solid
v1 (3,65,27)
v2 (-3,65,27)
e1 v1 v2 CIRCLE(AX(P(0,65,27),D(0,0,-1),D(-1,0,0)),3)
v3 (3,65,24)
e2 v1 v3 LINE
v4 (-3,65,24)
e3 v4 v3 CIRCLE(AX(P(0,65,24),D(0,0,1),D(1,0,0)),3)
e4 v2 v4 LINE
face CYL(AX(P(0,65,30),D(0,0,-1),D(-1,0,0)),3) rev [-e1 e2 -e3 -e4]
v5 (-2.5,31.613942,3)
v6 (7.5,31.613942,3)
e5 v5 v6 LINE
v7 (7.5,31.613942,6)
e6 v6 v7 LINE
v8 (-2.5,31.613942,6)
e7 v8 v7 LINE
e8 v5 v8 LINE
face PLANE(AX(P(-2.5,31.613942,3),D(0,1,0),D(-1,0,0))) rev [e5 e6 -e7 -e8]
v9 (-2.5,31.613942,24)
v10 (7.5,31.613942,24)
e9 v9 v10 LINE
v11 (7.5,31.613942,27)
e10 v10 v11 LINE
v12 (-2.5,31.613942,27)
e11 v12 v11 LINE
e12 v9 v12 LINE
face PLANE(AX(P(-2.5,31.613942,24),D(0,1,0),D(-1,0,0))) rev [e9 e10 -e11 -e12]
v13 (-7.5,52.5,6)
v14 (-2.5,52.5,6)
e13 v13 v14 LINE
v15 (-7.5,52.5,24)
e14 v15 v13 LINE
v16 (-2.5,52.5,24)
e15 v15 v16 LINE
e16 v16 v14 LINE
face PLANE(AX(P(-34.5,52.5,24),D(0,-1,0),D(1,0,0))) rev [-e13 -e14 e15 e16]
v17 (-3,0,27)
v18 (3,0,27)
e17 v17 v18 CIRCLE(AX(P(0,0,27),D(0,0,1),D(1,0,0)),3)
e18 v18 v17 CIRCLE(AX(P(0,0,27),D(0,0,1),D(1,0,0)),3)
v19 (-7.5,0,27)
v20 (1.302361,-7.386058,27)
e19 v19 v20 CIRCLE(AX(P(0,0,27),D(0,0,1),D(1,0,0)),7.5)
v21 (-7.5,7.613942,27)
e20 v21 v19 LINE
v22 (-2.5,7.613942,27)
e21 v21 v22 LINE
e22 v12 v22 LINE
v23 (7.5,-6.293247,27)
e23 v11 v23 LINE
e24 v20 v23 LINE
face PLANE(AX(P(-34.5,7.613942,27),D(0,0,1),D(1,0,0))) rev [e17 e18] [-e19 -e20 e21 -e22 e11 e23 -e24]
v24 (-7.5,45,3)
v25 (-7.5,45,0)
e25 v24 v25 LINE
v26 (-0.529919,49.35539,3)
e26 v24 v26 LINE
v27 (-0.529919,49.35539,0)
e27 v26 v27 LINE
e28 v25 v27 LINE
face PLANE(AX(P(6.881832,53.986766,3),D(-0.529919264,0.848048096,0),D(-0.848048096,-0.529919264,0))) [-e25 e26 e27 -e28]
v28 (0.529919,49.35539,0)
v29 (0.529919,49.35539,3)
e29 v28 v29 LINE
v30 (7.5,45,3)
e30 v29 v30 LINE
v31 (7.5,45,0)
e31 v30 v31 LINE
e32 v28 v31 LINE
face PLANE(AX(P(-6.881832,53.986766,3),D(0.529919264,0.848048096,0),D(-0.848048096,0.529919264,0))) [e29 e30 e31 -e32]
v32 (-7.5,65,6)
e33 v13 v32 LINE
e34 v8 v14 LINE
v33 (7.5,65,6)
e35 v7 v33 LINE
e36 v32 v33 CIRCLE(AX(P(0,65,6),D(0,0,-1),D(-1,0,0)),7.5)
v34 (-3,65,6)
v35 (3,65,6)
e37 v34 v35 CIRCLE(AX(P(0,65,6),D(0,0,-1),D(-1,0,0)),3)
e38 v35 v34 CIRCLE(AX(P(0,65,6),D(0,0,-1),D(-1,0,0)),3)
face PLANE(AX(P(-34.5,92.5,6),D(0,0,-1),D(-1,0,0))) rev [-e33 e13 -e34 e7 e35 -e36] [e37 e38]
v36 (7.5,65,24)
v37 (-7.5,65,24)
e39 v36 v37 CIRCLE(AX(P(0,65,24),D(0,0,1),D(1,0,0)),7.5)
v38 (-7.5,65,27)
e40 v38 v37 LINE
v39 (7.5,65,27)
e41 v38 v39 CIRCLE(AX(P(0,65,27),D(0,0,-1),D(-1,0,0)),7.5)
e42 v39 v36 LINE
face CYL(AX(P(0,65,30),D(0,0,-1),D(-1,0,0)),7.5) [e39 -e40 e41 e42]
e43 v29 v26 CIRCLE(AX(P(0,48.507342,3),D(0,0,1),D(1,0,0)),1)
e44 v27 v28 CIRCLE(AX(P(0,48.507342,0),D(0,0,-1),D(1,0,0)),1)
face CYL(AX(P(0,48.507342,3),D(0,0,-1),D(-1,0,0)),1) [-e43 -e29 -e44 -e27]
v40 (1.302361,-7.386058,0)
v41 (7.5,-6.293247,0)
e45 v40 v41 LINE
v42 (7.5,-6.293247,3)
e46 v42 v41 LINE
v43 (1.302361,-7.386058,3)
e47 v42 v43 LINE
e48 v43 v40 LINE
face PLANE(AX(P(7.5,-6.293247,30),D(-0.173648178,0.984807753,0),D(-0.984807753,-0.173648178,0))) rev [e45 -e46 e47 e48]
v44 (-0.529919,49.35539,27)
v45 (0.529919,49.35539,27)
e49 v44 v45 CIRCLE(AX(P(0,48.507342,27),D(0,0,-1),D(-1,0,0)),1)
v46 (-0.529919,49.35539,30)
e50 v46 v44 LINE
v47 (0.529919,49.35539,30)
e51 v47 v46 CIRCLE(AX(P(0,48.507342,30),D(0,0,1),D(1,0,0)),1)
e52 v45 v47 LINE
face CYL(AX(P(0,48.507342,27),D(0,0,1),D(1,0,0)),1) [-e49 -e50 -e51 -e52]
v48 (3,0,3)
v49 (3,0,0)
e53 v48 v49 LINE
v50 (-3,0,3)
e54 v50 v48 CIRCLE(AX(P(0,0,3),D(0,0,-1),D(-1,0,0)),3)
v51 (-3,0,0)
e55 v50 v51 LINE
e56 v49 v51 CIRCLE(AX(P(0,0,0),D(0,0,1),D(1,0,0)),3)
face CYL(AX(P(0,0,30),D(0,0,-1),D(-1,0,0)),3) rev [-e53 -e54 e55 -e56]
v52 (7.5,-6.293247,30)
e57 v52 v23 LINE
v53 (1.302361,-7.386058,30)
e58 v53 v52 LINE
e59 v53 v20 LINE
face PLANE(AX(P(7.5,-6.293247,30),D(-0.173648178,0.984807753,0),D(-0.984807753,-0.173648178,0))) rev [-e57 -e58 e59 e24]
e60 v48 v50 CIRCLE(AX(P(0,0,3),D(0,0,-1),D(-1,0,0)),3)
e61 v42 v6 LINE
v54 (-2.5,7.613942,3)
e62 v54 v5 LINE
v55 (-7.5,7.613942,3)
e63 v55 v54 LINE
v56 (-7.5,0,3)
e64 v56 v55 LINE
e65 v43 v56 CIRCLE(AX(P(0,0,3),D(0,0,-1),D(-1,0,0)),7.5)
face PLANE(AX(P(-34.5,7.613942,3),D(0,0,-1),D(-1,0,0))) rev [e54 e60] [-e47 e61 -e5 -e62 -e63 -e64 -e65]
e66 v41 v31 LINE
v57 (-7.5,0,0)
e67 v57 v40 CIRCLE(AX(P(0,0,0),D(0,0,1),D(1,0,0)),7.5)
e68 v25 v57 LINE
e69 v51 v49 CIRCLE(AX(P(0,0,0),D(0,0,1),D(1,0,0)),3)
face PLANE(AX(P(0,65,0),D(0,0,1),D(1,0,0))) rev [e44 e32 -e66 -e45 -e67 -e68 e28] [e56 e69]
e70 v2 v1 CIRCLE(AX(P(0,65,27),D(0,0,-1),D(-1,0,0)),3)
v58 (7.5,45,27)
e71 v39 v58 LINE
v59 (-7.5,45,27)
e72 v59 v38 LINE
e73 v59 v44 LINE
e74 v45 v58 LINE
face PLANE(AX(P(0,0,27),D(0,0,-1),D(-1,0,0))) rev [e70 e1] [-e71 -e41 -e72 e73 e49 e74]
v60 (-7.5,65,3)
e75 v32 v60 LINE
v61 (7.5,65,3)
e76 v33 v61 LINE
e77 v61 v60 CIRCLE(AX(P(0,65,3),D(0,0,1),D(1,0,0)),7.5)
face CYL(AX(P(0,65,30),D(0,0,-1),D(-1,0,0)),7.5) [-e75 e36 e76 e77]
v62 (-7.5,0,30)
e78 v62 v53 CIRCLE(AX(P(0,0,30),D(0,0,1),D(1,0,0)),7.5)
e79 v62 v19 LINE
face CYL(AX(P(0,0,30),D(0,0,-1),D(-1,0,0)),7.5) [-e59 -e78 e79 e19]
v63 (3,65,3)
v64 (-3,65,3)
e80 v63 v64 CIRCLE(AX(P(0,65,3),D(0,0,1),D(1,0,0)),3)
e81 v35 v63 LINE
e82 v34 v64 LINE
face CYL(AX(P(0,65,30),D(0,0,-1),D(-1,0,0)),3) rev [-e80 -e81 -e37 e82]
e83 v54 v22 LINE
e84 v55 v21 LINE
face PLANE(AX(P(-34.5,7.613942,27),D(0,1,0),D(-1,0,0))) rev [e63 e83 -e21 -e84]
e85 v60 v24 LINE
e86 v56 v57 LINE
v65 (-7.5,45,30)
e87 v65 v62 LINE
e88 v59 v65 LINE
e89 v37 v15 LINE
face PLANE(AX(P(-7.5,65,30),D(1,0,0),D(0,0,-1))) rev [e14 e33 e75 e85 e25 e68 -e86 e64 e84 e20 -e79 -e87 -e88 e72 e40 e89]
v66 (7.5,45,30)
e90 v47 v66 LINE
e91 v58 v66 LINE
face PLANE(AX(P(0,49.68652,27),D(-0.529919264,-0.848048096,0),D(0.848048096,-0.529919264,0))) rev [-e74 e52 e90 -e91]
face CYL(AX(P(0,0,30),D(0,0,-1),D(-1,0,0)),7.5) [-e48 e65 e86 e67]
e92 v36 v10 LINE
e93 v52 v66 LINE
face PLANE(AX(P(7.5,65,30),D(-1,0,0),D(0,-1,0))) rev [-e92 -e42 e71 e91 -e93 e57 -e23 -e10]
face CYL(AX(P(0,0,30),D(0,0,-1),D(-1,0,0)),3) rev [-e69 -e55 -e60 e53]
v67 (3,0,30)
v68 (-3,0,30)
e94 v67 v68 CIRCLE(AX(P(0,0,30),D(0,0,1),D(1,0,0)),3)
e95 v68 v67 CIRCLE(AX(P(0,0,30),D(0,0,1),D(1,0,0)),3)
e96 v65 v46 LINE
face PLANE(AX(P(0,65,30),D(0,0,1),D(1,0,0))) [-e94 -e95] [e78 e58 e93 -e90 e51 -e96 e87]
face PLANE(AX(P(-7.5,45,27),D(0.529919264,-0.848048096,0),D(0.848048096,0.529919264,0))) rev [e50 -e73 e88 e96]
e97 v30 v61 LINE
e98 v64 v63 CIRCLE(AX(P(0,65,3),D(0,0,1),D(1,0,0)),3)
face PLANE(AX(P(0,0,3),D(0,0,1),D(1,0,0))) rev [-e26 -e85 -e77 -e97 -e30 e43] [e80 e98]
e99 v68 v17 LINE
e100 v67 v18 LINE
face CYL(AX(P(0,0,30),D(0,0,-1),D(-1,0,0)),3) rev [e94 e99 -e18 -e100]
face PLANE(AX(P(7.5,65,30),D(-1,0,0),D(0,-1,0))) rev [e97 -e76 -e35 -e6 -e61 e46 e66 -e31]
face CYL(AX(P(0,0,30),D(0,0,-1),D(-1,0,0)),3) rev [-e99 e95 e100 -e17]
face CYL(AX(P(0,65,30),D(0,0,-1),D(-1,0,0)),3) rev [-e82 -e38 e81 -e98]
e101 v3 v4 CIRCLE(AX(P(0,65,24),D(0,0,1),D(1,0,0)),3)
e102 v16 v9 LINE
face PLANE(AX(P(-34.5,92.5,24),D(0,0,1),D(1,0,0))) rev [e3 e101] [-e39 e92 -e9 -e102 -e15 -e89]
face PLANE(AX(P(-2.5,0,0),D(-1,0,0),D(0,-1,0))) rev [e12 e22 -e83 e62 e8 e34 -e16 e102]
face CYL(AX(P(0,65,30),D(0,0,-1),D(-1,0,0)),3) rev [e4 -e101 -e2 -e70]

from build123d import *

# Parameters (mm, degrees)
SKETCH1_R           = 3
BOSS_EXTRUDE1_DEPTH = 30
SKETCH2_W           = 24
SKETCH2_H           = 30
SKETCH2_W_2         = 18
SKETCH2_H_2         = 40
CUT_EXTRUDE1_DEPTH  = 42
CUT_EXTRUDE2_DEPTH  = 3
CUT_EXTRUDE3_START  = -30
CUT_EXTRUDE3_DEPTH  = 3
FILLET1_R           = 1
CUT_EXTRUDE4_DEPTH  = 10


with BuildPart() as part:
    # Sketch1 → Boss-Extrude1 (new body)
    with BuildSketch(Plane.XY):
        with BuildLine():
            Line((-7.5, 65), (-7.5, 0))
            ThreePointArc((-7.5, 0), (-4.820907073, -5.745333323), (1.302361333, -7.386058148))
            Line((1.302361333, -7.386058148), (7.5, -6.293247234))
            Line((7.5, -6.293247234), (7.5, 65))
            ThreePointArc((7.5, 65), (0, 72.5), (-7.5, 65))
        make_face()
        Circle(SKETCH1_R, mode=Mode.SUBTRACT)
        with Locations((0, 65)):
            Circle(SKETCH1_R, mode=Mode.SUBTRACT)
    extrude(amount=BOSS_EXTRUDE1_DEPTH)

    # Sketch2 → Cut-Extrude1 (cut)
    with BuildSketch(Plane(origin=(7.5, 0, 0), x_dir=(0, 0, -1), z_dir=(1, 0, 0))):
        with Locations((-15, -7.386058148)):
            Rectangle(SKETCH2_W, SKETCH2_H)
        with Locations((-15, 72.5)):
            Rectangle(SKETCH2_W_2, SKETCH2_H_2)
    extrude(amount=-CUT_EXTRUDE1_DEPTH, mode=Mode.SUBTRACT)

    # Sketch3<2> → Cut-Extrude2 (cut)
    with BuildSketch(Plane.XY.offset(30)):
        Polygon((-7.5, 45), (0, 49.686520139), (7.5, 45), (7.5, 48.622120254), (18.624271708, 48.622120254), (18.624271708, 113.745401459), (-18.624271708, 113.745401459), (-18.624271708, 48.622120254), (-7.5, 48.622120254), align=None)
    extrude(amount=-CUT_EXTRUDE2_DEPTH, mode=Mode.SUBTRACT)

    # 草图3<2> → Cut-Extrude3 (cut)
    with BuildSketch(Plane.XY.offset(30).offset(CUT_EXTRUDE3_START)):
        Polygon((-7.5, 45), (0, 49.686520139), (7.5, 45), (7.5, 48.622120254), (18.624271708, 48.622120254), (18.624271708, 113.745401459), (-18.624271708, 113.745401459), (-18.624271708, 48.622120254), (-7.5, 48.622120254), align=None)
    extrude(amount=CUT_EXTRUDE3_DEPTH, mode=Mode.SUBTRACT)

    # Fillet1
    fillet1_edges = [part.edges().sort_by_distance(p)[0] for p in [
        (0, 49.686520139, 1.5),
        (0, 49.686520139, 28.5),
    ]]
    fillet(fillet1_edges, radius=FILLET1_R)

    # Sketch4 → Cut-Extrude4 (cut)
    with BuildSketch(Plane(origin=(7.5, 0, 0), x_dir=(0, 0, -1), z_dir=(1, 0, 0))):
        Polygon((-3, -16.386058148), (-27, -16.386058148), (-27, 31.613941852), (-24, 31.613941852), (-24, 73.386058148), (-6, 73.386058148), (-6, 31.613941852), (-3, 31.613941852), align=None)
    extrude(amount=-CUT_EXTRUDE4_DEPTH, mode=Mode.SUBTRACT)


solid = part.part
